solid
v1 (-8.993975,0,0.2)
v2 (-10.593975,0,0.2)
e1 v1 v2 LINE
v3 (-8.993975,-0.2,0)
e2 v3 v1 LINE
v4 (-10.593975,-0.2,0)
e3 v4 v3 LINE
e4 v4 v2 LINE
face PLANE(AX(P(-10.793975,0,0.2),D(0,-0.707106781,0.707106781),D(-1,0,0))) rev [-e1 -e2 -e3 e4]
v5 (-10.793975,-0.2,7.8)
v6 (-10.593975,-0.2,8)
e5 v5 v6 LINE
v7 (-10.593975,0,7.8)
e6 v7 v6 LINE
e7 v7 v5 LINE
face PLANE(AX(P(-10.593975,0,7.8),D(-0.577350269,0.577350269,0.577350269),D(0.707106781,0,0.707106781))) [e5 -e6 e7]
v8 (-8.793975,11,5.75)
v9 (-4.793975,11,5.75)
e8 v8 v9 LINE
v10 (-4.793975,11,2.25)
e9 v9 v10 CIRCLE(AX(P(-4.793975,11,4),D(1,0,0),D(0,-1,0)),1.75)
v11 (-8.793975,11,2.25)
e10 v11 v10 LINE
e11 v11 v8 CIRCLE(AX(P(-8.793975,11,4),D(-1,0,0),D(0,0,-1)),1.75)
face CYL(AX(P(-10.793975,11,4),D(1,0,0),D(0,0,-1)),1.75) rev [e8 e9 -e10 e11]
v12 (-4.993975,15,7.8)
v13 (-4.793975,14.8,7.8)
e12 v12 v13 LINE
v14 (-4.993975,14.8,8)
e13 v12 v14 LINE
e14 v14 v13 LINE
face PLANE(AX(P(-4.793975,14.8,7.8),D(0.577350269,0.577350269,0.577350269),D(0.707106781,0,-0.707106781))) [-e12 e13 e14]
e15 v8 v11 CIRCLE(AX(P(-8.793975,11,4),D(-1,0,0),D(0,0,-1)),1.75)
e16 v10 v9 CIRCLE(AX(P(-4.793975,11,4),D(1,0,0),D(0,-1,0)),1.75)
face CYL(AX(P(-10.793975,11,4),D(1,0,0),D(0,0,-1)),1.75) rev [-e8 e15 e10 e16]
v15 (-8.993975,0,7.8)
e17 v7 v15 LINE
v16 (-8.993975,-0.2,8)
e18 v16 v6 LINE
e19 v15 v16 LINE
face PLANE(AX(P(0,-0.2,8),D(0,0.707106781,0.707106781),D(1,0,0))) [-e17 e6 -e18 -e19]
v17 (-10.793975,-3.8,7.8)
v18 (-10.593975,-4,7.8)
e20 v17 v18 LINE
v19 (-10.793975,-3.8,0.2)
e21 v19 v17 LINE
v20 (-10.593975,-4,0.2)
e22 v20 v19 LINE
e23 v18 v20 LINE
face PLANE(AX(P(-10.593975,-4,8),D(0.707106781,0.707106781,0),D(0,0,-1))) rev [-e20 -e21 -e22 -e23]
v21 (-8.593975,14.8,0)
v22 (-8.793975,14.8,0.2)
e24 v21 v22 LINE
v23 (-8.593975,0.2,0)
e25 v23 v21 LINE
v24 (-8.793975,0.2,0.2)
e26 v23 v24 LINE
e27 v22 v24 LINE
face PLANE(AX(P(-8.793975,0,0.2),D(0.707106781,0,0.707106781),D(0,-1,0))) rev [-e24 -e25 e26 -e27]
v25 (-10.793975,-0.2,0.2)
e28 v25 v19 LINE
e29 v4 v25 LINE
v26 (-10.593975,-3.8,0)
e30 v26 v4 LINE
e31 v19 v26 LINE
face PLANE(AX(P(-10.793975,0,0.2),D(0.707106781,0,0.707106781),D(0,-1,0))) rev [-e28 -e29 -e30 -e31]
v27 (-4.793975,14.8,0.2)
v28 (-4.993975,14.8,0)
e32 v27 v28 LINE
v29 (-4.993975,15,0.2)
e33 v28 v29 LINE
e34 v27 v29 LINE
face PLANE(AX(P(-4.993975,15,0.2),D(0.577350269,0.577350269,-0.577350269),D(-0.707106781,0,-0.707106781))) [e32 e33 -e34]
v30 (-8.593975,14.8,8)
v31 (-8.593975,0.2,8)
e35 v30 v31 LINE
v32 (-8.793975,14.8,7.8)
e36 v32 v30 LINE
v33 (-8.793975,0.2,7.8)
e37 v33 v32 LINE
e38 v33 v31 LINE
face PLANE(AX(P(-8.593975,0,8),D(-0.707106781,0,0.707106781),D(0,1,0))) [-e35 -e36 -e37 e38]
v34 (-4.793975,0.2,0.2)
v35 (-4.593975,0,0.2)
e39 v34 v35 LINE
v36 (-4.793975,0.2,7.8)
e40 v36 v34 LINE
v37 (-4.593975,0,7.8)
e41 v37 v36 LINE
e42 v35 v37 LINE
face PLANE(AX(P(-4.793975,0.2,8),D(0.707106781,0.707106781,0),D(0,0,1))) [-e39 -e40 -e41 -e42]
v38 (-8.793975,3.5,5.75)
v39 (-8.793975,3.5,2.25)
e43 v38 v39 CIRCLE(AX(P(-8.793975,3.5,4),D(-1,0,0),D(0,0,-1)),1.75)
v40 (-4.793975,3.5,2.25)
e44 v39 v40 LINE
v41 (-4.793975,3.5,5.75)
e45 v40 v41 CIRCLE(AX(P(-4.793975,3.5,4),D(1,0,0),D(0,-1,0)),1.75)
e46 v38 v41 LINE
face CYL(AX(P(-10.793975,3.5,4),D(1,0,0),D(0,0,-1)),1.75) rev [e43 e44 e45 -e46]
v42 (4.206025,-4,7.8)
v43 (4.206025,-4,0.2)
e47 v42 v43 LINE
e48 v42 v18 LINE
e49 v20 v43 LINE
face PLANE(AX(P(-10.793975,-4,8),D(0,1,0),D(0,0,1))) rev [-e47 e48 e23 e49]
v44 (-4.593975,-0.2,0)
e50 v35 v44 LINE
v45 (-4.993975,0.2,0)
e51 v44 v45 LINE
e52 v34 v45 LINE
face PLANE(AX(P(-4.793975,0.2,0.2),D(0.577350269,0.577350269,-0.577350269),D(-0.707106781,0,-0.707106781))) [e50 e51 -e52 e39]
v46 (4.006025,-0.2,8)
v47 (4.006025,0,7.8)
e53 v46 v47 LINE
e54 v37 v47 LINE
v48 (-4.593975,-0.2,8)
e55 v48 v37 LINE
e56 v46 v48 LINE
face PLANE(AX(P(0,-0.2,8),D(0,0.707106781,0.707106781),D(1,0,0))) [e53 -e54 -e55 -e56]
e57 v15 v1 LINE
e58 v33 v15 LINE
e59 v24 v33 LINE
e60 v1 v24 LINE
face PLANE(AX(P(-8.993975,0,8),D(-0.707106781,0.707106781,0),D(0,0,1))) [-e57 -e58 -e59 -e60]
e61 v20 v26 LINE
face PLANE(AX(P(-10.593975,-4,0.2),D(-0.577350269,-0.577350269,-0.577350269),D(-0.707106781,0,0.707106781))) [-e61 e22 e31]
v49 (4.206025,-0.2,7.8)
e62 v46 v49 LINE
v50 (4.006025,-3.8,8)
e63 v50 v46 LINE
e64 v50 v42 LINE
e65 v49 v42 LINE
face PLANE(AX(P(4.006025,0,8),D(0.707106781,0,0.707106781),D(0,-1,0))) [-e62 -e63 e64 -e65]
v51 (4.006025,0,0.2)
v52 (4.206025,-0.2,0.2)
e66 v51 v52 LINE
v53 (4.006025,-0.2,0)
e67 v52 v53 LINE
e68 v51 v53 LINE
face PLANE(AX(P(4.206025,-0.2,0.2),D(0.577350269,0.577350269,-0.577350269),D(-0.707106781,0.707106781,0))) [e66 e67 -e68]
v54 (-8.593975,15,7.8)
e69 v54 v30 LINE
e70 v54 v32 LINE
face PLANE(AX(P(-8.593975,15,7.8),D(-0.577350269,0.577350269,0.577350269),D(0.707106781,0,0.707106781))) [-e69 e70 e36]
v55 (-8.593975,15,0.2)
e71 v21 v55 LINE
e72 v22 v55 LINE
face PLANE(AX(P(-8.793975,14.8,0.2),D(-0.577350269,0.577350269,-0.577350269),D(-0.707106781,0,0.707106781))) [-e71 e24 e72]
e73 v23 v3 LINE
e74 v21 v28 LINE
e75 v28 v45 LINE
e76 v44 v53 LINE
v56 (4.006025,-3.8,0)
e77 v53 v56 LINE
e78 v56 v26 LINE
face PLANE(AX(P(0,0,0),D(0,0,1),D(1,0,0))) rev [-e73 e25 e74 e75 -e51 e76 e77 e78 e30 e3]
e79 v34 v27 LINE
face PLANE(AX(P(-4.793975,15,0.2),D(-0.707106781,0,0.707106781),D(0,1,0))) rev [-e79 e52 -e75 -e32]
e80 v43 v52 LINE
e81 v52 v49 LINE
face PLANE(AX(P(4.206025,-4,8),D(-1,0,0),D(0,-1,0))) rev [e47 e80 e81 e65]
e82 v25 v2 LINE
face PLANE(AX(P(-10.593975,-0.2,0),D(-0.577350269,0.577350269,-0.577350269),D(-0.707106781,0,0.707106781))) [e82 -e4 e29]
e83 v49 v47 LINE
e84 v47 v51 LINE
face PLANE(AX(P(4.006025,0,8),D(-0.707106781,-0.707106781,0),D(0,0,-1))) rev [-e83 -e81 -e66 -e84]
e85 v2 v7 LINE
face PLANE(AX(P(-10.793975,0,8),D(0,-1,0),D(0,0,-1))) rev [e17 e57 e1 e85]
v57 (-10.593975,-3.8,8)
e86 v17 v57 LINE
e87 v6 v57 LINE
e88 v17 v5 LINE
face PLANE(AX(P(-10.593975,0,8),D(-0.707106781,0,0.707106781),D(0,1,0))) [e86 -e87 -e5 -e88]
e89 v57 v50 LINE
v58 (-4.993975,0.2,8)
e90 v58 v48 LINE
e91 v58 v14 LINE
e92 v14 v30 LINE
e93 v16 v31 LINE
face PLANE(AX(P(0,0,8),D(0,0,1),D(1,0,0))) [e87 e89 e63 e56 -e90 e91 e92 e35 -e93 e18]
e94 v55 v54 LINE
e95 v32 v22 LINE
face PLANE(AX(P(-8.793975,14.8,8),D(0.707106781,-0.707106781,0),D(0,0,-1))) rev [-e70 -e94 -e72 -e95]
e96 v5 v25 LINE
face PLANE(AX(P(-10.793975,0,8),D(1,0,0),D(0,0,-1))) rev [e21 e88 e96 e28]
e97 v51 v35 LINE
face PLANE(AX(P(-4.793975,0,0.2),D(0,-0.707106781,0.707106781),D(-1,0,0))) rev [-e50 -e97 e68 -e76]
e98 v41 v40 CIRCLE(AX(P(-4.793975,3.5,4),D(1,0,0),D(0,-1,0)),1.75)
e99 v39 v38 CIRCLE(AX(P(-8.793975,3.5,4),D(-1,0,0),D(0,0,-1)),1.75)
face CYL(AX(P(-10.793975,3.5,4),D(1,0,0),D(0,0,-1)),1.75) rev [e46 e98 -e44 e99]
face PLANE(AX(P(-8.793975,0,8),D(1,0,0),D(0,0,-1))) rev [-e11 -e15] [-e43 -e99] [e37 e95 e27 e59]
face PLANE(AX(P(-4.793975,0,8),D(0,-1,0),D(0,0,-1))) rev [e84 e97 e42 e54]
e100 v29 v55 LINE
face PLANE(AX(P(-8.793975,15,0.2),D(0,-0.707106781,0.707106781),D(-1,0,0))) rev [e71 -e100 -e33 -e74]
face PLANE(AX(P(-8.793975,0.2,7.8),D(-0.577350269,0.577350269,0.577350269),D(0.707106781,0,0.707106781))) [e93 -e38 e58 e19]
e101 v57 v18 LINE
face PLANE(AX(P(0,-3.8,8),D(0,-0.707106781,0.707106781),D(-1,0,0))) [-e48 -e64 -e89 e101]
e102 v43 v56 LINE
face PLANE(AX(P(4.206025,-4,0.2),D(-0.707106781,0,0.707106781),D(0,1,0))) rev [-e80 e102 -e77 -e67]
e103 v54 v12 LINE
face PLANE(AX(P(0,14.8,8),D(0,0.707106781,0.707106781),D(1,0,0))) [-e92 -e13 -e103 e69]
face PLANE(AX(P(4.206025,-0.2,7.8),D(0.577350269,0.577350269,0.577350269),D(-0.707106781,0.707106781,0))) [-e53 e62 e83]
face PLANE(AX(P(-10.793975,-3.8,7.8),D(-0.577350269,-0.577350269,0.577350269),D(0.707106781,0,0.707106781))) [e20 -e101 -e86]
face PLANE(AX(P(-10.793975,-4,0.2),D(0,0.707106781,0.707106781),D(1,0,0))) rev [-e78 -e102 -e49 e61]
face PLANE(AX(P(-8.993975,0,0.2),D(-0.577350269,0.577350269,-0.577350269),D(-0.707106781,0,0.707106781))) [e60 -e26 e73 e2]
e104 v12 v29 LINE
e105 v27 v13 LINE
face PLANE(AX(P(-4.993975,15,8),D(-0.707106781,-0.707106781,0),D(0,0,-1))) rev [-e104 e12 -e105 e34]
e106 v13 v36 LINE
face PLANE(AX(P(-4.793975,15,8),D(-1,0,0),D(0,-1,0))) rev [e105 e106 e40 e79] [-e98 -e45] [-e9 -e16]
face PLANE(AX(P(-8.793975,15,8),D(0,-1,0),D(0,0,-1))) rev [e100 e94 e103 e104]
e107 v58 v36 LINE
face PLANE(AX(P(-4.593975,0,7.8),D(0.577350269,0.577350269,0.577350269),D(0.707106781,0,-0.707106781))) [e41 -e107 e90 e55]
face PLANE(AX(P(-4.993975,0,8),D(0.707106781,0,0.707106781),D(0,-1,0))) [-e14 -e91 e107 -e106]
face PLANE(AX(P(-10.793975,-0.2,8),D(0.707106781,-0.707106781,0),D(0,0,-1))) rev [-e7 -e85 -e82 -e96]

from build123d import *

# Parameters (mm, degrees)
BOSS_EXTRUDE1_DEPTH            = 8
CHAMFER1_SIZE                  = 0.2
CUT_EXTRUDE1_REACH             = 23.401
SKETCH4_R                      = 1.75
CUT_EXTRUDE1_DIRECTION_2_DEPTH = 22.400934559


with BuildPart() as part:
    # Sketch2 → Boss-Extrude1 (new body)
    with BuildSketch(Plane.XY):
        Polygon((-10.793974552, 0), (-8.793974552, 0), (-8.793974552, 15), (-4.793974552, 15), (-4.793974552, 0), (4.206025448, 0), (4.206025448, -4), (-10.793974552, -4), align=None)
    extrude(amount=BOSS_EXTRUDE1_DEPTH)

    # Chamfer1
    chamfer1_edges = [part.edges().sort_by_distance(p)[0] for p in [
        (-0.293974552, 0, 0),
        (4.206025448, -2, 0),
        (-3.293974552, -4, 0),
        (-10.793974552, -2, 0),
        (4.206025448, -2, 8),
        (-10.793974552, 0, 4),
        (-8.793974552, 0, 4),
        (-8.793974552, 15, 4),
        (-4.793974552, 15, 4),
        (-4.793974552, 0, 4),
        (4.206025448, 0, 4),
        (-10.793974552, -4, 4),
        (-0.293974552, 0, 8),
        (-4.793974552, 7.5, 8),
        (-6.793974552, 15, 8),
        (-8.793974552, 7.5, 8),
        (-9.793974552, 0, 8),
        (-10.793974552, -2, 8),
        (-9.793974552, 0, 0),
        (-3.293974552, -4, 8),
        (-8.793974552, 7.5, 0),
        (-6.793974552, 15, 0),
        (-4.793974552, 7.5, 0),
    ]]
    chamfer(chamfer1_edges, length=CHAMFER1_SIZE)

    # Sketch4 → Cut-Extrude1 (cut, up to next)
    with BuildSketch(Plane.ZY.offset(8.793974552), mode=Mode.PRIVATE) as cut_extrude1_sk1:
        with Locations(Location((4, 11, 0), (0, 0, 180))):
            Circle(SKETCH4_R)
    cut_extrude1_tool1 = extrude(cut_extrude1_sk1.sketch, amount=-CUT_EXTRUDE1_REACH, mode=Mode.PRIVATE) & part.part
    # Sketch4 → Cut-Extrude1 (cut, up to next)
    with BuildSketch(Plane.ZY.offset(8.793974552), mode=Mode.PRIVATE) as cut_extrude1_sk2:
        with Locations(Location((4, 3.5, 0), (0, 0, 180))):
            Circle(SKETCH4_R)
    cut_extrude1_tool2 = extrude(cut_extrude1_sk2.sketch, amount=-CUT_EXTRUDE1_REACH, mode=Mode.PRIVATE) & part.part
    add(cut_extrude1_tool1.solids().sort_by_distance((-8.793975, 11, 4))[0], mode=Mode.SUBTRACT)
    add(cut_extrude1_tool2.solids().sort_by_distance((-8.793975, 3.5, 4))[0], mode=Mode.SUBTRACT)

    # Sketch4 → Cut-Extrude1 direction 2 (cut)
    with BuildSketch(Plane.ZY.offset(8.793974552)):
        with Locations(Location((4, 11, 0), (0, 0, 180))):
            Circle(SKETCH4_R)
        with Locations(Location((4, 3.5, 0), (0, 0, 180))):
            Circle(SKETCH4_R)
    extrude(amount=CUT_EXTRUDE1_DIRECTION_2_DEPTH, mode=Mode.SUBTRACT)


solid = part.part
